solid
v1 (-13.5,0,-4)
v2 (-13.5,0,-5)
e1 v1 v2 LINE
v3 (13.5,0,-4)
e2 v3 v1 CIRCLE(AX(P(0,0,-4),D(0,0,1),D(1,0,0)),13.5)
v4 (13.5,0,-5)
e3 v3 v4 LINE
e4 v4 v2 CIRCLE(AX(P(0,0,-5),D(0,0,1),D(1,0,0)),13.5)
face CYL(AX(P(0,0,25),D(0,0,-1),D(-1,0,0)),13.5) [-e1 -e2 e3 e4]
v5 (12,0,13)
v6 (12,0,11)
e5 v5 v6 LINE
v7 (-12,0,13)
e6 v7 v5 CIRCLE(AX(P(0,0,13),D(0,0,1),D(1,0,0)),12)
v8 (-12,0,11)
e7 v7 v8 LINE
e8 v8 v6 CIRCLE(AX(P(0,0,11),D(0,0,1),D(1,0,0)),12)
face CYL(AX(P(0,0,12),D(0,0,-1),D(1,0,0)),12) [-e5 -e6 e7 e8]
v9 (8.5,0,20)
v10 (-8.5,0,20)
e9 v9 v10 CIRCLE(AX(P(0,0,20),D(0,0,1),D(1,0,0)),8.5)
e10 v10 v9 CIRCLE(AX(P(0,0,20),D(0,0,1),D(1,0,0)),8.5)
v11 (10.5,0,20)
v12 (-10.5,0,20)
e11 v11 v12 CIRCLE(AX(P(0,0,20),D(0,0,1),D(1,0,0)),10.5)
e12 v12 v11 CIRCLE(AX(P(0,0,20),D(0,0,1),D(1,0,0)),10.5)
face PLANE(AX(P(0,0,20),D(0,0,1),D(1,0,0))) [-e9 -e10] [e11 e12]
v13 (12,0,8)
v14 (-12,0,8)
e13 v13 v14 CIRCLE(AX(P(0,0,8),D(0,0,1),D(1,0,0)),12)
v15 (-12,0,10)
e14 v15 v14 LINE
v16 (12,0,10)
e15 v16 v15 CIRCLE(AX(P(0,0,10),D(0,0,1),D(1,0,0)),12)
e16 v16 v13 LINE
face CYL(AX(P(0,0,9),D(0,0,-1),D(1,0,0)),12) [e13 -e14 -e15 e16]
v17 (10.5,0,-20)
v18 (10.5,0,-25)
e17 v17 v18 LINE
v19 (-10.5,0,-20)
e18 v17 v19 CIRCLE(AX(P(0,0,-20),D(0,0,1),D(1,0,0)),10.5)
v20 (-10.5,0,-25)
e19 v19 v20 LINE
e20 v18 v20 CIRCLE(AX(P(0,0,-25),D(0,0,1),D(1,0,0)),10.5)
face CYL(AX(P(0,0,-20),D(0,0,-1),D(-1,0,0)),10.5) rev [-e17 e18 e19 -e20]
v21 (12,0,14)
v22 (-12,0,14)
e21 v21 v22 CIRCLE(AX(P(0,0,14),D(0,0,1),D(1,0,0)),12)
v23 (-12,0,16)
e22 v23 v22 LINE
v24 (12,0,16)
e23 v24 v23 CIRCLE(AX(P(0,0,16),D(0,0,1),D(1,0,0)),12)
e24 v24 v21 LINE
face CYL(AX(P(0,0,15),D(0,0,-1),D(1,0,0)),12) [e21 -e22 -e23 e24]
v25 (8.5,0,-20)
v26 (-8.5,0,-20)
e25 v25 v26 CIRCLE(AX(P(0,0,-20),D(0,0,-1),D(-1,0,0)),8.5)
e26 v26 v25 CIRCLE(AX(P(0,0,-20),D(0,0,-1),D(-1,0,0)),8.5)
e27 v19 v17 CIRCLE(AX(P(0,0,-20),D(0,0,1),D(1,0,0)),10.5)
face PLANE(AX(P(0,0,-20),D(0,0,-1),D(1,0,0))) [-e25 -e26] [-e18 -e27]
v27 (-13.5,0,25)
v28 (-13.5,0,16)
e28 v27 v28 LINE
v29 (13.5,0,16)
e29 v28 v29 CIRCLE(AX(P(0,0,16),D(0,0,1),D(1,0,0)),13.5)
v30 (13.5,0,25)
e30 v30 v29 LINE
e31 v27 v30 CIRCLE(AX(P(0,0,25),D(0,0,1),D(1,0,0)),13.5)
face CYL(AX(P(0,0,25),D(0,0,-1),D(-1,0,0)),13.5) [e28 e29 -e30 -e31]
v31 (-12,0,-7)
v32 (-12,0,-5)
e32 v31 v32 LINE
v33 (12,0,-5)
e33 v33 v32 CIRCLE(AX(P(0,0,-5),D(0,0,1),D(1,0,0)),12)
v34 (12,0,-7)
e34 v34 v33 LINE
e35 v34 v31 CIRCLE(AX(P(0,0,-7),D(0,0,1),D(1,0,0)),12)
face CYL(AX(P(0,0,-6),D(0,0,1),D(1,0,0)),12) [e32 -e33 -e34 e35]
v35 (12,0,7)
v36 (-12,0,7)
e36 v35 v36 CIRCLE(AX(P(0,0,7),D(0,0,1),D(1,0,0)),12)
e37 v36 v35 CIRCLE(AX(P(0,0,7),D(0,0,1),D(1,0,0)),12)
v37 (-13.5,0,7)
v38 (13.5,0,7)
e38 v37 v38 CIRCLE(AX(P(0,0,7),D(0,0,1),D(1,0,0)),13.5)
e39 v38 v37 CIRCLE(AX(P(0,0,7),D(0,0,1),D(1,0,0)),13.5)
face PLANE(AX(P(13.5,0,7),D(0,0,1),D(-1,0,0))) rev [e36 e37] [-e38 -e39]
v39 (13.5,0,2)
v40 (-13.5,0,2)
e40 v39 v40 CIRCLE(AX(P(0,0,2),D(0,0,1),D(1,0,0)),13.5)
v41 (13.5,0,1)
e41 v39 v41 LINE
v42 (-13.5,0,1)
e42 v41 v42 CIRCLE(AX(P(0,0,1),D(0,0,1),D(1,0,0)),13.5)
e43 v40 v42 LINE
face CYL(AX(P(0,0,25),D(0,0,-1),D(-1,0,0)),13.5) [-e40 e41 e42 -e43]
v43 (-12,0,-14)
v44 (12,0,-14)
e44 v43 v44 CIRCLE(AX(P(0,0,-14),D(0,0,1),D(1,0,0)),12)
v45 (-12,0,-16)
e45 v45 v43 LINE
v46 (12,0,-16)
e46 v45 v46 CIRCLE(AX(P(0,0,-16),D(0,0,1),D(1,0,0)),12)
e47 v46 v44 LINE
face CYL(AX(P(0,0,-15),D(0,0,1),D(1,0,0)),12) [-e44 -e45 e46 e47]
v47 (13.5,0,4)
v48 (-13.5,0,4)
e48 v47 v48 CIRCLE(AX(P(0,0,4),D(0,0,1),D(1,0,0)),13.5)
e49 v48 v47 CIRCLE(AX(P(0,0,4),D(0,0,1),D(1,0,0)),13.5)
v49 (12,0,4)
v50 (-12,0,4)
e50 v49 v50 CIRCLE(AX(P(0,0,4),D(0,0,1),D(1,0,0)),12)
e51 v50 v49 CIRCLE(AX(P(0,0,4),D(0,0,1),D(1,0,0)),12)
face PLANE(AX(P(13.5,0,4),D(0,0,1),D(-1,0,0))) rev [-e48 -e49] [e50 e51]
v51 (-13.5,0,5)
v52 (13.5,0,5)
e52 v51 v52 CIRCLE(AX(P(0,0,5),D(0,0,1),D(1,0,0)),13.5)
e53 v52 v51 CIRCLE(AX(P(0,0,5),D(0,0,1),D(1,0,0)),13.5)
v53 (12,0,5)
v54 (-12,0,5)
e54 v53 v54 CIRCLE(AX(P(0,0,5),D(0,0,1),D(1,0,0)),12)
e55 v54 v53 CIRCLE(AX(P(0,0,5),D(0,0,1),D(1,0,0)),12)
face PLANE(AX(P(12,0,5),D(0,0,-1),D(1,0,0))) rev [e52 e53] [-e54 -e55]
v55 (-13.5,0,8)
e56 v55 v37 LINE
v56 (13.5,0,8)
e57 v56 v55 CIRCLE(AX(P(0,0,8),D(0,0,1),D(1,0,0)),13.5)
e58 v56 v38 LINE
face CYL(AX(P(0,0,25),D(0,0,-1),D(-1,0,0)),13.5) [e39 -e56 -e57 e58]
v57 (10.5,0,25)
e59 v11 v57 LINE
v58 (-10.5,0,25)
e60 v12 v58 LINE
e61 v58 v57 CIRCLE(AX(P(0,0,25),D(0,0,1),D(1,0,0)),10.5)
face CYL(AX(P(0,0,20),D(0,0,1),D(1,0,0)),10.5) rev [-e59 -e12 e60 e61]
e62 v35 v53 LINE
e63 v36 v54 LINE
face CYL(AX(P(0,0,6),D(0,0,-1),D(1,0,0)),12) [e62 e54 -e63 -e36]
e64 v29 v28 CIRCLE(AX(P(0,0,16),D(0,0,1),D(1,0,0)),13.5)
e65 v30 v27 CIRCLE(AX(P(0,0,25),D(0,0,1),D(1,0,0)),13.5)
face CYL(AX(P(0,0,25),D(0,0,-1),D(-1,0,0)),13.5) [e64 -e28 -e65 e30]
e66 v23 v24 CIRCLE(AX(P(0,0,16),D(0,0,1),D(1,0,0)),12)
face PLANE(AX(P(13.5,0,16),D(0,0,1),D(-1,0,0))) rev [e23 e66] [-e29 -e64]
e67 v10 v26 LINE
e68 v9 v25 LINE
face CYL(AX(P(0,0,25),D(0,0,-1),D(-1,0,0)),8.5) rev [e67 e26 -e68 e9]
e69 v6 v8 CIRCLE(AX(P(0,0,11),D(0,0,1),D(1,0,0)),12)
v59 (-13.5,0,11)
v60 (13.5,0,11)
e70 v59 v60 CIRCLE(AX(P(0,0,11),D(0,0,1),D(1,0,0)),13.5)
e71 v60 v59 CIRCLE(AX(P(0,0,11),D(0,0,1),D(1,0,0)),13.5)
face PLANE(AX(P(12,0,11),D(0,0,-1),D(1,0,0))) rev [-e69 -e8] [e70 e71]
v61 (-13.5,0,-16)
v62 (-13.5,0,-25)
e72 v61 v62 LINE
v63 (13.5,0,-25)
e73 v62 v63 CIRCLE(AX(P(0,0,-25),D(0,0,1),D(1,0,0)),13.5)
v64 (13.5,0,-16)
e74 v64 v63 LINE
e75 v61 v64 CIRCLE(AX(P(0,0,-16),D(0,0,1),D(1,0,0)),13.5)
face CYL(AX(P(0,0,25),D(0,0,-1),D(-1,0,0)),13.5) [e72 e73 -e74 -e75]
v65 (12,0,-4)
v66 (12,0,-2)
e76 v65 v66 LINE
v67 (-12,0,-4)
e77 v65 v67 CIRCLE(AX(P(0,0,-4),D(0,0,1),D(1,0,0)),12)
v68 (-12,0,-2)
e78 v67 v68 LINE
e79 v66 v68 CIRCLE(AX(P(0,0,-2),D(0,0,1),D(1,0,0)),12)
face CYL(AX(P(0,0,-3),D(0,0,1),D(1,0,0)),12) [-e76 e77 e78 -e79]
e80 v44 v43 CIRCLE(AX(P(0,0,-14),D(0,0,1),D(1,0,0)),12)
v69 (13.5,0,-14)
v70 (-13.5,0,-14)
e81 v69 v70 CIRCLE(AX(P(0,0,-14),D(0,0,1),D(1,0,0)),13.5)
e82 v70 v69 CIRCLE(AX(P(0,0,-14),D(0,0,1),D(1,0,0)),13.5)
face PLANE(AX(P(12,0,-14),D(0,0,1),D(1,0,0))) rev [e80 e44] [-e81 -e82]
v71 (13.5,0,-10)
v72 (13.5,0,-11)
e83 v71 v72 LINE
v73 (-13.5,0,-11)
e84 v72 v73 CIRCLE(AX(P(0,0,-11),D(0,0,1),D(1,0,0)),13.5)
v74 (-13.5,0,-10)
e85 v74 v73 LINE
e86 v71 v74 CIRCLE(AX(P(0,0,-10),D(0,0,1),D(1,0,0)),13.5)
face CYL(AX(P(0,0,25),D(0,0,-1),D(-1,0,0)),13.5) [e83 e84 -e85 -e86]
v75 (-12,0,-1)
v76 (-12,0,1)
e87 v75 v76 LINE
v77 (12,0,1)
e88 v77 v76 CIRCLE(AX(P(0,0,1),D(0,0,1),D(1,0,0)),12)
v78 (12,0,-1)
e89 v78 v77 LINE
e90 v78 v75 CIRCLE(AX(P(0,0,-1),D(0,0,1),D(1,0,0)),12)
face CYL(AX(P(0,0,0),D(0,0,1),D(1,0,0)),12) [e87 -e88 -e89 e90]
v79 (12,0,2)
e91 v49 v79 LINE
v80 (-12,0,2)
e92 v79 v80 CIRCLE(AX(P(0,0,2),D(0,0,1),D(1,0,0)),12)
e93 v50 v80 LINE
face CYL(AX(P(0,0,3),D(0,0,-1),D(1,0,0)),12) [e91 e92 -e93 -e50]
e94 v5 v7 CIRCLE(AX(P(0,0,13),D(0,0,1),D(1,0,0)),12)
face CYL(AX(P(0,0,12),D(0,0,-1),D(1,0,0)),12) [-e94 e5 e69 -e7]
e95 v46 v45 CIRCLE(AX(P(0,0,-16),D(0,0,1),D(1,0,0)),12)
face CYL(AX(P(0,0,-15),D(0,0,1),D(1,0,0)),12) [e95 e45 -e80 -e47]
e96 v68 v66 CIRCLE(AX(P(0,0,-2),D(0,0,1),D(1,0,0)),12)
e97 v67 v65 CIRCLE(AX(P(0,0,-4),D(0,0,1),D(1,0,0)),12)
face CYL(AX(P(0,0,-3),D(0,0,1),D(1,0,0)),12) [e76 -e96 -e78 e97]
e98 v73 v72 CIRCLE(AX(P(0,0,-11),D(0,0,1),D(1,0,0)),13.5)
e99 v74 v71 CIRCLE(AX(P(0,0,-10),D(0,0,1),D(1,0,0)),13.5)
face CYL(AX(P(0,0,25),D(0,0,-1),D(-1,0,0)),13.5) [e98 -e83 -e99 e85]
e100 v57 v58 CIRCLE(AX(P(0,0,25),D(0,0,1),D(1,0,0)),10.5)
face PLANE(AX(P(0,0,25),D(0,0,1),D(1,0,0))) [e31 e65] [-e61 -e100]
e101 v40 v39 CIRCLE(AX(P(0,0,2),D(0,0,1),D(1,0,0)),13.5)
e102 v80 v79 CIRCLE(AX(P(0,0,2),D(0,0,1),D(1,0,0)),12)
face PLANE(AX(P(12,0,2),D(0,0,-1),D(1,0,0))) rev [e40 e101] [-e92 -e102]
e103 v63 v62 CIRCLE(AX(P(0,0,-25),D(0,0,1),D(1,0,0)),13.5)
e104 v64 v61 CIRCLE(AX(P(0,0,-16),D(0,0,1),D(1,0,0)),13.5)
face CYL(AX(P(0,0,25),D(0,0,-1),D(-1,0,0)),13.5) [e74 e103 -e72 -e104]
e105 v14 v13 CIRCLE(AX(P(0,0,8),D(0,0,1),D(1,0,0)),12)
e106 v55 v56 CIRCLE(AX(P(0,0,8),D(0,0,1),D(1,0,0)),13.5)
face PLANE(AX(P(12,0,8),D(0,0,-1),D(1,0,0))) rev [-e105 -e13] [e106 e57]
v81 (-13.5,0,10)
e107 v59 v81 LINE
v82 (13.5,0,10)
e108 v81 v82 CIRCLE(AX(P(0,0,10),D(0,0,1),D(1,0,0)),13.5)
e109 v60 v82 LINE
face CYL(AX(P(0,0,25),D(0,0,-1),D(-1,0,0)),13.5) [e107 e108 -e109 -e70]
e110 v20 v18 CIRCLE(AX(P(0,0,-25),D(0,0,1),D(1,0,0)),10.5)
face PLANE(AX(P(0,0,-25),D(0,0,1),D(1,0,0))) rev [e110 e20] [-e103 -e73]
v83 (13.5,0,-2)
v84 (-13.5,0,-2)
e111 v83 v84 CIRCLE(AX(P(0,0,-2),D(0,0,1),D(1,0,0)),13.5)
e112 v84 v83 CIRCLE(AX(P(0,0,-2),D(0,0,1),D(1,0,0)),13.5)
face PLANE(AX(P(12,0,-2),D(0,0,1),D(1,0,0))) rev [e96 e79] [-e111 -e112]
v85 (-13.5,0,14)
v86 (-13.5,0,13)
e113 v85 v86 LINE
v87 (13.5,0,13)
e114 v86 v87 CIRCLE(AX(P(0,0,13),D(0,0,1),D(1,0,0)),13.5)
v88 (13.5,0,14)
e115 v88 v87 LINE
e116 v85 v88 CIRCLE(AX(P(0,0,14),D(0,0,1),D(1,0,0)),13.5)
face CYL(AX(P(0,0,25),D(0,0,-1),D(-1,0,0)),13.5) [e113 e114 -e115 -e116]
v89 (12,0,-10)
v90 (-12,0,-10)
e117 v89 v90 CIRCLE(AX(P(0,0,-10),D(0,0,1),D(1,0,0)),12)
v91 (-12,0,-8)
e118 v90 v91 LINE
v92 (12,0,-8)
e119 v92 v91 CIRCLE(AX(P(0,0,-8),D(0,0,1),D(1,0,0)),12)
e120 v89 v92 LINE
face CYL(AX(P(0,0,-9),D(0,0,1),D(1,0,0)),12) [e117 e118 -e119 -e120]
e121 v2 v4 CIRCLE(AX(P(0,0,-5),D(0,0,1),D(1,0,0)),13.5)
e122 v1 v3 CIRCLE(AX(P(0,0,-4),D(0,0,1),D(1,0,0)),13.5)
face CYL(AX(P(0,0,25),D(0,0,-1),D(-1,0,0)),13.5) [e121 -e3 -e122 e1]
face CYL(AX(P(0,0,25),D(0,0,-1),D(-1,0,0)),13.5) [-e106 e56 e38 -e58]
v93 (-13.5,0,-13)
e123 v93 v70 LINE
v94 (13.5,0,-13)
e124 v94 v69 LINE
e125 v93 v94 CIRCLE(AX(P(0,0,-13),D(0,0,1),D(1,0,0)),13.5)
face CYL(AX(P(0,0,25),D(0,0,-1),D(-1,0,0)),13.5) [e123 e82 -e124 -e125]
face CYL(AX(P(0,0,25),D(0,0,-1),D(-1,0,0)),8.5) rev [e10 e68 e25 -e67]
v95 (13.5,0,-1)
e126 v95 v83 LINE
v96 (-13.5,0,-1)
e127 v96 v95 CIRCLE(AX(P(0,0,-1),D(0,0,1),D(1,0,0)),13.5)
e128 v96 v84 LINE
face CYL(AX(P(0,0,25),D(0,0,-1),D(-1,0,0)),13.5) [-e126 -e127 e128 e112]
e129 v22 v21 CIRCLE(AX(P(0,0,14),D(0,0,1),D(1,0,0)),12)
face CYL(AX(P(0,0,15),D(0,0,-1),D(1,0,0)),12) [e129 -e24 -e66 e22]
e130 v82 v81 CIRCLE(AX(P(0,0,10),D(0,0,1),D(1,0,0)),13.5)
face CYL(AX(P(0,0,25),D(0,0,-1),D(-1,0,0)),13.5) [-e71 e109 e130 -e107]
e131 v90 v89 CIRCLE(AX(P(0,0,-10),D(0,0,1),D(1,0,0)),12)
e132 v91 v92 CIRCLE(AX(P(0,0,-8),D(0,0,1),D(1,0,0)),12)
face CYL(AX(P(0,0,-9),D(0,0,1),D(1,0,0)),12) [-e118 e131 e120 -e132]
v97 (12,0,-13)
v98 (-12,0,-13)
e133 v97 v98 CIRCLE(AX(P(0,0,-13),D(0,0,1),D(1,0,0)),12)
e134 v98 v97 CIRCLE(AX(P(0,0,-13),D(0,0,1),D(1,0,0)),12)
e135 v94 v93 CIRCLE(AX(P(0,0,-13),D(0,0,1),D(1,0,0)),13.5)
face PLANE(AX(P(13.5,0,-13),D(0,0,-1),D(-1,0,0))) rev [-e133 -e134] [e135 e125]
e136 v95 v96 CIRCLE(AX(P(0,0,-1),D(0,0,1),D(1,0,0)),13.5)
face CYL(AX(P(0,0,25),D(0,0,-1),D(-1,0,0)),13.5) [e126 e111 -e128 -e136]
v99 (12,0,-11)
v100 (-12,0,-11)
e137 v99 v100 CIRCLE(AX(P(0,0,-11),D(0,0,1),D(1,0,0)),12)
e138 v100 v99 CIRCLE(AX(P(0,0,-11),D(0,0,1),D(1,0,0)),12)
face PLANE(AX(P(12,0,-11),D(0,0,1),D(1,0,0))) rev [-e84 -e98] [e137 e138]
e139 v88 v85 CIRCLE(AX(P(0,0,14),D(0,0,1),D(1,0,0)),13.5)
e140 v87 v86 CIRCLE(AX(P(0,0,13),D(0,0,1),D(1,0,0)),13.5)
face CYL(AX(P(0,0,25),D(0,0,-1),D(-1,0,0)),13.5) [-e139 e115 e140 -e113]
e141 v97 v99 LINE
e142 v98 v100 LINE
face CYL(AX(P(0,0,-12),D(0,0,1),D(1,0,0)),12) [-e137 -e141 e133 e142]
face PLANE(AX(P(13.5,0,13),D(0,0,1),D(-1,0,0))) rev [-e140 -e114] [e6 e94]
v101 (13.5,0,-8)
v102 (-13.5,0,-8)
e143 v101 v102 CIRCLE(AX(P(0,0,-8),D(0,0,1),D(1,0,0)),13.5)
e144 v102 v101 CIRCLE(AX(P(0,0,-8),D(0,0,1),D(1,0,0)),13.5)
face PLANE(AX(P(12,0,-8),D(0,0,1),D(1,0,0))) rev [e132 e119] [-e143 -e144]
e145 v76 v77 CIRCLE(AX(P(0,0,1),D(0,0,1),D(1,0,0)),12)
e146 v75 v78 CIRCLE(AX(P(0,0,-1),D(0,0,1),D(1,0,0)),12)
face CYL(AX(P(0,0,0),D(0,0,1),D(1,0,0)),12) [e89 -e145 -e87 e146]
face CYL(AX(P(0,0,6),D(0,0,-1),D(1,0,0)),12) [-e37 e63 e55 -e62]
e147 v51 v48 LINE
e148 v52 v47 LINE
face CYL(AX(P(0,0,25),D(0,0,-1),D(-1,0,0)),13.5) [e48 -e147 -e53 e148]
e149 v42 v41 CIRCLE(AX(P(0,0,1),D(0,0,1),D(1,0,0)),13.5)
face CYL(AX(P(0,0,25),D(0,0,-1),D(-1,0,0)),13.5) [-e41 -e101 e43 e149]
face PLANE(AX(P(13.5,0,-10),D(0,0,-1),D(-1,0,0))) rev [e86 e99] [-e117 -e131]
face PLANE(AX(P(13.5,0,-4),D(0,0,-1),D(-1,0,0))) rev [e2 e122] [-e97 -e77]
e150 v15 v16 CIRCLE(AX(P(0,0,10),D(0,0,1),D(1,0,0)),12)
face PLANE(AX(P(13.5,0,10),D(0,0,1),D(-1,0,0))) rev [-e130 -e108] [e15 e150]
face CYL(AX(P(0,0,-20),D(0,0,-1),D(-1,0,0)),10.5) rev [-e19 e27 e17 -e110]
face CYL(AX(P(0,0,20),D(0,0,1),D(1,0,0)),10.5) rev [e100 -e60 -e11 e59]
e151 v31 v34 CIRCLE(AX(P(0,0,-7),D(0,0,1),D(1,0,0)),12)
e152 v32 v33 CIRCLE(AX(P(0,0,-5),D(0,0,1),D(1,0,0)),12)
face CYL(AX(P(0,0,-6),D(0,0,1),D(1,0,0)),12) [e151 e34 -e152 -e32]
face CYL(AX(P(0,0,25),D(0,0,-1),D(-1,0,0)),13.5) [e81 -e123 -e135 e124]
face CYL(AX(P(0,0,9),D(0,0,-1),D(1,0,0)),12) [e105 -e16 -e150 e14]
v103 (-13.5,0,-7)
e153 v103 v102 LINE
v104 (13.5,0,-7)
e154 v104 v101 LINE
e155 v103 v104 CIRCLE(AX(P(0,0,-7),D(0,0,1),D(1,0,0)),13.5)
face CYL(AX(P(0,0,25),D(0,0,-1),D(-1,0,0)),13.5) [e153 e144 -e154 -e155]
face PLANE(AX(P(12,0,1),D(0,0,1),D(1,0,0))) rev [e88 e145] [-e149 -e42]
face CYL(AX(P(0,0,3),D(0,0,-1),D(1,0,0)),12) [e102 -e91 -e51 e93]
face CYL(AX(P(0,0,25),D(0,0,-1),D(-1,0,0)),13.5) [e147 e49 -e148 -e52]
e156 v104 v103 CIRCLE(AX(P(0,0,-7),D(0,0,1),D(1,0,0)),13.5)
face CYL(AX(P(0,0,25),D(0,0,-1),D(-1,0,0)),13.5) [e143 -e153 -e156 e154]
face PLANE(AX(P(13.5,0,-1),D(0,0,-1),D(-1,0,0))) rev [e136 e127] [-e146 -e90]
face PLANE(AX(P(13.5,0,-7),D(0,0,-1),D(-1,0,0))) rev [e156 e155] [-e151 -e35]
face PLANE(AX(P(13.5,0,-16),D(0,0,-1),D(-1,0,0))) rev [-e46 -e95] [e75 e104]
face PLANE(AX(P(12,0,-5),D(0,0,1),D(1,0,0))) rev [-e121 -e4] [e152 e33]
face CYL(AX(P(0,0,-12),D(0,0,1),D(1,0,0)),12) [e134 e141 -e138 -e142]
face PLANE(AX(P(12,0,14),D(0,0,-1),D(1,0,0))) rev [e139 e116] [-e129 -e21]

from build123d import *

# Parameters (mm, degrees)
SKETCH_1_R               = 13.5
SKETCH_1_R_2             = 8.5
EXTRUDE_1_DEPTH          = 25
SKETCH_2_W               = 1.5
SKETCH_2_H               = 2
PATTERN_LINEAR_1_COUNT   = 6
PATTERN_LINEAR_1_PITCH   = 3
MIRROR_1_COPY_1_SKETCH_W = 1.5
MIRROR_1_COPY_1_SKETCH_H = 2
MIRROR_1_COPY_2_SKETCH_W = 1.5
MIRROR_1_COPY_2_SKETCH_H = 2
MIRROR_1_COPY_3_SKETCH_W = 1.5
MIRROR_1_COPY_3_SKETCH_H = 2
MIRROR_1_COPY_4_SKETCH_W = 1.5
MIRROR_1_COPY_4_SKETCH_H = 2
MIRROR_1_COPY_5_SKETCH_W = 1.5
MIRROR_1_COPY_5_SKETCH_H = 2
MIRROR_1_COPY_6_SKETCH_W = 1.5
MIRROR_1_COPY_6_SKETCH_H = 2
SKETCH_3_R               = 10.5
CUT_EXTRUDE_1_DEPTH      = 5


with BuildPart() as part:
    # 草图1 → 凸台-拉伸1 (new, symmetric)
    with BuildSketch(Plane.XY):
        Circle(SKETCH_1_R)
        Circle(SKETCH_1_R_2, mode=Mode.SUBTRACT)
    extrude(amount=EXTRUDE_1_DEPTH, both=True)

    # 草图2 → 切除-旋转1 (revolve, cut)
    with BuildSketch(Plane(origin=(0, 0, 0), x_dir=(1, 0, 0), z_dir=(0, 1, 0))):
        with Locations((12.75, 0)):
            Rectangle(SKETCH_2_W, SKETCH_2_H)
    cut_revolve_1 = revolve(axis=Axis((0, 0, 0), (0, 0, -1)), mode=Mode.SUBTRACT)

    # 阵列(线性)1: 切除-旋转1 ×6
    with Locations(*[(0, 0, -i * PATTERN_LINEAR_1_PITCH) for i in range(1, PATTERN_LINEAR_1_COUNT)]):
        add(cut_revolve_1, mode=Mode.SUBTRACT)

    # 镜向1 copy 1 sketch → 镜向1 copy 1 (revolve, cut)
    with BuildSketch(Plane(origin=(0, 0, 3), x_dir=(1, 0, 0), z_dir=(0, 1, 0))):
        with Locations((12.75, 0)):
            Rectangle(MIRROR_1_COPY_1_SKETCH_W, MIRROR_1_COPY_1_SKETCH_H)
    revolve(axis=Axis((0, 0, 3), (0, 0, -1)), mode=Mode.SUBTRACT)

    # 镜向1 copy 2 sketch → 镜向1 copy 2 (revolve, cut)
    with BuildSketch(Plane(origin=(0, 0, 6), x_dir=(1, 0, 0), z_dir=(0, 1, 0))):
        with Locations((12.75, 0)):
            Rectangle(MIRROR_1_COPY_2_SKETCH_W, MIRROR_1_COPY_2_SKETCH_H)
    revolve(axis=Axis((0, 0, 6), (0, 0, -1)), mode=Mode.SUBTRACT)

    # 镜向1 copy 3 sketch → 镜向1 copy 3 (revolve, cut)
    with BuildSketch(Plane(origin=(0, 0, 9), x_dir=(1, 0, 0), z_dir=(0, 1, 0))):
        with Locations((12.75, 0)):
            Rectangle(MIRROR_1_COPY_3_SKETCH_W, MIRROR_1_COPY_3_SKETCH_H)
    revolve(axis=Axis((0, 0, 9), (0, 0, -1)), mode=Mode.SUBTRACT)

    # 镜向1 copy 4 sketch → 镜向1 copy 4 (revolve, cut)
    with BuildSketch(Plane(origin=(0, 0, 12), x_dir=(1, 0, 0), z_dir=(0, 1, 0))):
        with Locations((12.75, 0)):
            Rectangle(MIRROR_1_COPY_4_SKETCH_W, MIRROR_1_COPY_4_SKETCH_H)
    revolve(axis=Axis((0, 0, 12), (0, 0, -1)), mode=Mode.SUBTRACT)

    # 镜向1 copy 5 sketch → 镜向1 copy 5 (revolve, cut)
    with BuildSketch(Plane(origin=(0, 0, 15), x_dir=(1, 0, 0), z_dir=(0, 1, 0))):
        with Locations((12.75, 0)):
            Rectangle(MIRROR_1_COPY_5_SKETCH_W, MIRROR_1_COPY_5_SKETCH_H)
    revolve(axis=Axis((0, 0, 15), (0, 0, -1)), mode=Mode.SUBTRACT)

    # 镜向1 copy 6 sketch → 镜向1 copy 6 (revolve, cut)
    with BuildSketch(Plane(origin=(0, 0, 0), x_dir=(1, 0, 0), z_dir=(0, 1, 0))):
        with Locations((12.75, 0)):
            Rectangle(MIRROR_1_COPY_6_SKETCH_W, MIRROR_1_COPY_6_SKETCH_H)
    revolve(axis=Axis((0, 0, 0), (0, 0, -1)), mode=Mode.SUBTRACT)

    # 草图3 → 切除-拉伸1 (cut)
    with BuildSketch(Plane.XY.offset(25)):
        Circle(SKETCH_3_R)
    cut_extrude_1 = extrude(amount=-CUT_EXTRUDE_1_DEPTH, mode=Mode.SUBTRACT)

    # 镜向2: 切除-拉伸1 across plane
    add(cut_extrude_1.mirror(Plane.XY), mode=Mode.SUBTRACT)


solid = part.part
